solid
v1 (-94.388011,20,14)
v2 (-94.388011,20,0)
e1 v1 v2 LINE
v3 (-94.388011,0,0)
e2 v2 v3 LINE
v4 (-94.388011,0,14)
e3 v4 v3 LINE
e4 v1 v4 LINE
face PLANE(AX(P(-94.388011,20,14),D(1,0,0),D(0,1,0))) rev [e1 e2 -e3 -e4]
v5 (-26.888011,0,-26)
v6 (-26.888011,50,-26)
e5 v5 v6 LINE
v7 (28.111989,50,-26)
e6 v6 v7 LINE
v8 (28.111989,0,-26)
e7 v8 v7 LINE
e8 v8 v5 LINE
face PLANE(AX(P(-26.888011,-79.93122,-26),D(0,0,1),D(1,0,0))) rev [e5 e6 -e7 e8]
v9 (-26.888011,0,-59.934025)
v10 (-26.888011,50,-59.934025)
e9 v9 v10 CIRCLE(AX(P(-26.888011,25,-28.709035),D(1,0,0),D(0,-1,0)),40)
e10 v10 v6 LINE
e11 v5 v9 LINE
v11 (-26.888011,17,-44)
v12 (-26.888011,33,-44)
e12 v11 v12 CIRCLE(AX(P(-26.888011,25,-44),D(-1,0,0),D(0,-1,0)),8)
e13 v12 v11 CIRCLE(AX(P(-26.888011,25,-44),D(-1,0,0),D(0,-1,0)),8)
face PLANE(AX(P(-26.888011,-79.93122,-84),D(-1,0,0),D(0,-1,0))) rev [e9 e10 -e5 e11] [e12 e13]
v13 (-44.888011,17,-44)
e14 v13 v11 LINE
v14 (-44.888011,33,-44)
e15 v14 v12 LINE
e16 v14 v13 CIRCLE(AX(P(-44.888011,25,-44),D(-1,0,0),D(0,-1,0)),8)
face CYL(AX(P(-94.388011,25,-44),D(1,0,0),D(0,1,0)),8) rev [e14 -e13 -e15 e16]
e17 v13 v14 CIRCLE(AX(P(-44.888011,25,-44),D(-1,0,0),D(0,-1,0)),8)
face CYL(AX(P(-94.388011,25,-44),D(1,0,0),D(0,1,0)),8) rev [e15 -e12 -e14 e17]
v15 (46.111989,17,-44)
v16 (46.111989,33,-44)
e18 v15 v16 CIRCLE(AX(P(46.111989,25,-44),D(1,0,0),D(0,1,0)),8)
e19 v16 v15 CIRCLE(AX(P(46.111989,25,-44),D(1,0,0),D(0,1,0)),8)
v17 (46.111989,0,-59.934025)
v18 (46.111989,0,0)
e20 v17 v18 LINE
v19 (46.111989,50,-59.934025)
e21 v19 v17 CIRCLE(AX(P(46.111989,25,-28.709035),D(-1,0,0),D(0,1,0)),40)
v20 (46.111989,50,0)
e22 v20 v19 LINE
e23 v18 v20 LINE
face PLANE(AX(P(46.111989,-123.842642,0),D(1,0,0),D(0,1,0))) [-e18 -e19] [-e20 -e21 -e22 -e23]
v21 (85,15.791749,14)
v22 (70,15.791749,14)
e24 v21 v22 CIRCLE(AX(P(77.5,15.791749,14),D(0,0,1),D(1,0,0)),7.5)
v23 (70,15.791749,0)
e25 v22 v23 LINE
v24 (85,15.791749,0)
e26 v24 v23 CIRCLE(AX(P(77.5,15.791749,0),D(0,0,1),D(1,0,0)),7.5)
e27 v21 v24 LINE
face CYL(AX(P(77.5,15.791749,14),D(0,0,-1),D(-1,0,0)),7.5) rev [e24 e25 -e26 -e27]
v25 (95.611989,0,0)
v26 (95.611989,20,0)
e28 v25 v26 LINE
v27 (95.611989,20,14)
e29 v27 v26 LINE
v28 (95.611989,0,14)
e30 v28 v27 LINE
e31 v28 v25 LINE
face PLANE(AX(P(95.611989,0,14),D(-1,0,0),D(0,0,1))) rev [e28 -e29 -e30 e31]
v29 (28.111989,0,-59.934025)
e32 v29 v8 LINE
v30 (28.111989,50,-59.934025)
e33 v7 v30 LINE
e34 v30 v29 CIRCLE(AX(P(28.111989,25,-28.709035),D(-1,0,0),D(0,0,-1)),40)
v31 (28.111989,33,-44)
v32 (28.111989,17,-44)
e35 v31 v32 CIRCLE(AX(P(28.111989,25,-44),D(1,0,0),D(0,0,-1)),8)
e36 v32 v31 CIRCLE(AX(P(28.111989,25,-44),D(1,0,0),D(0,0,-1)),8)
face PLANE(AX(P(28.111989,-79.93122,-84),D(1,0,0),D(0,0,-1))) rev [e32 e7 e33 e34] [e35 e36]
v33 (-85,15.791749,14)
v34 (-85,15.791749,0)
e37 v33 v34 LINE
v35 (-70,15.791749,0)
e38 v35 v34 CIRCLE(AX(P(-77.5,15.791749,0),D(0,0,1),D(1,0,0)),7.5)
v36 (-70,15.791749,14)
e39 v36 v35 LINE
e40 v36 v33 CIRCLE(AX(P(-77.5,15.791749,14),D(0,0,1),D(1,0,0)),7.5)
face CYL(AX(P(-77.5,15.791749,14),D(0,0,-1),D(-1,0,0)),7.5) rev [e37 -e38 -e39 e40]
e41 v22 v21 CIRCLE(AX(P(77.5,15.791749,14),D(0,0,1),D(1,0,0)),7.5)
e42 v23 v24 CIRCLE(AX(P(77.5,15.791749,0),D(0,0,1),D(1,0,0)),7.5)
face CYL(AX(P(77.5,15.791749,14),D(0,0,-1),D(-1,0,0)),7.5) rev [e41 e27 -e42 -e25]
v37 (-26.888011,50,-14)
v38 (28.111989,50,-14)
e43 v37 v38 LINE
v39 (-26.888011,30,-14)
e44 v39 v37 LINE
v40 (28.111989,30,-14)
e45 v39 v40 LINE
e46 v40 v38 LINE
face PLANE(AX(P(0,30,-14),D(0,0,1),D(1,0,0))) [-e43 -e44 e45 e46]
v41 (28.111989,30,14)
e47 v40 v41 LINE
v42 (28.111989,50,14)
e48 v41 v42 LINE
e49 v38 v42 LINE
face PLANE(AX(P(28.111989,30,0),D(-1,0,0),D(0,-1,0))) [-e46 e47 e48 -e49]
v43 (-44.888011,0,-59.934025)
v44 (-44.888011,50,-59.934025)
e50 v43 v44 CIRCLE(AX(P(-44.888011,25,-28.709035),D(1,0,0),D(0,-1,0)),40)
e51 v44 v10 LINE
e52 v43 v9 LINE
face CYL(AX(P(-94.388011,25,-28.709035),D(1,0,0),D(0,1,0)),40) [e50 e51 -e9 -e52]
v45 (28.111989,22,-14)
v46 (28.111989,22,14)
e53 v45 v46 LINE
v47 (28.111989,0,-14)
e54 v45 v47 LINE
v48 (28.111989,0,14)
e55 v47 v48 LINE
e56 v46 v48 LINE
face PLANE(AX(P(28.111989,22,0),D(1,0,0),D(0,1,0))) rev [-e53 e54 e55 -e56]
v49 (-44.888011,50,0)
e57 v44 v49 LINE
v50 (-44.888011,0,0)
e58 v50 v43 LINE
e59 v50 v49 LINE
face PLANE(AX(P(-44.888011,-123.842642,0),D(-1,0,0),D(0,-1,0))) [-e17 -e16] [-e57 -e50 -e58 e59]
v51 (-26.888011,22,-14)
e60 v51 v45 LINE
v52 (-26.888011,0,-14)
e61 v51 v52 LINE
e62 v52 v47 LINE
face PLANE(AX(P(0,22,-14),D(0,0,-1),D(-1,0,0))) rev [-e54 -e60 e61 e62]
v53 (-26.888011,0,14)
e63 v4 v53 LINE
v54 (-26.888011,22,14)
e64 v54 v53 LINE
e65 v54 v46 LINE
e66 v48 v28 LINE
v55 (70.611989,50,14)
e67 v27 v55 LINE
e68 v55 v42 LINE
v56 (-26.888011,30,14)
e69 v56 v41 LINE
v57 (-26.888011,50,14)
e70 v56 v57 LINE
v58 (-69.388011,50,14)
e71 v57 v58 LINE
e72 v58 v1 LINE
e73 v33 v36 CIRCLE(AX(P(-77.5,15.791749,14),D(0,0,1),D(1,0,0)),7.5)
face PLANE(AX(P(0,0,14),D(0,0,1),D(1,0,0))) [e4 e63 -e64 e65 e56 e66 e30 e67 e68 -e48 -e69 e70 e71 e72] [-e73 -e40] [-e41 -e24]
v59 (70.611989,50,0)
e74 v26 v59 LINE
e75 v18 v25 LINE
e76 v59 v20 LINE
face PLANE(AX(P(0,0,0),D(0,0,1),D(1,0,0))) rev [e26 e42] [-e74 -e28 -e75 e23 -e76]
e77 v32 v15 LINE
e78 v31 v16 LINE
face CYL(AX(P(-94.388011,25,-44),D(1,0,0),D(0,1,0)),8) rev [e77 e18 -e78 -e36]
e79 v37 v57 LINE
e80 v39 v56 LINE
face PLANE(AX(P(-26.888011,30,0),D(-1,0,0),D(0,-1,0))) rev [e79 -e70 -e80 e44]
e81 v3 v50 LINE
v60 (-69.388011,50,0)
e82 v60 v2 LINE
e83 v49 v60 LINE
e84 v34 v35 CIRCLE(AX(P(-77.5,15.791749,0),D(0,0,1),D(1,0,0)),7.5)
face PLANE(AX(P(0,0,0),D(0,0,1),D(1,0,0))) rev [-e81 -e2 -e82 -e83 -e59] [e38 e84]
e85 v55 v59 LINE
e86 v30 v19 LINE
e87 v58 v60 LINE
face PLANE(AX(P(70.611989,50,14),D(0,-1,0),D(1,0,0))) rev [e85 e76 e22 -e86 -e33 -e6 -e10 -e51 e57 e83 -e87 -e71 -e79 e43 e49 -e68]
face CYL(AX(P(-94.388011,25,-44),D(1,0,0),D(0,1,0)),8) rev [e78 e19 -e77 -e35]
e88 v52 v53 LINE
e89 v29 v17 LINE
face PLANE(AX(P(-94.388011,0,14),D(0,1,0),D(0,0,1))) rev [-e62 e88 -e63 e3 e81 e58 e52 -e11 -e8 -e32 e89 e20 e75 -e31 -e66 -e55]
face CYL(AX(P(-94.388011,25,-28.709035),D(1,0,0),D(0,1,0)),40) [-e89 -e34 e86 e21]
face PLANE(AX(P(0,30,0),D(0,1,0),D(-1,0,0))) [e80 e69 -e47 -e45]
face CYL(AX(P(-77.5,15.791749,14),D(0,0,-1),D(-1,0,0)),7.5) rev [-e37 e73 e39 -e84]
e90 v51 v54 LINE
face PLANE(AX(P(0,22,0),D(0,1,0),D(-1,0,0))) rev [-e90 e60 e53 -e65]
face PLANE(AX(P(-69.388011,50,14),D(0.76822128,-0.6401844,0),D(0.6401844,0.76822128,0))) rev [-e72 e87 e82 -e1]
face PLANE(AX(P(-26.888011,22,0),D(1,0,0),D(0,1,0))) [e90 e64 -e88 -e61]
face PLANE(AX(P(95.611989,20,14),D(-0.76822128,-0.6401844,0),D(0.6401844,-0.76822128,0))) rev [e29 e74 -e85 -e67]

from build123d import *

# Parameters (mm, degrees)
LUG_PLATE_PROFILE_SKETCH_R   = 7.5
LUG_PLATE_PROFILE_14MM_DEPTH = 14
CROSS_BLOCK_SKETCH_W         = 91
CROSS_BLOCK_SKETCH_H         = 84
CROSS_BLOCK_91X84_DEPTH      = 50
CENTRE_POCKET_SKETCH_W       = 55
CENTRE_POCKET_SKETCH_H       = 58
CENTRE_POCKET_55X58_DEPTH    = 50
CLEARANCE_CUT_SKETCH_R       = 8
CLEARANCE_CUT_DEPTH          = 172.161473469
LUG_PIN_HOLES_SKETCH_W       = 55
LUG_PIN_HOLES_SKETCH_H       = 28
LUG_PIN_HOLE_CUT_20MM_DEPTH  = 20
LUG_START                    = -50
SKETCH7_4_W                  = 55
SKETCH7_4_H                  = 28
LUG_PIN_HOLE_CUT_22MM_DEPTH  = 22


with BuildPart() as part:
    # Lug Plate Profile Sketch → Lug Plate Profile 14mm (new body)
    with BuildSketch(Plane.XY):
        Polygon((-94.388010718, 0), (95.611989282, 0), (95.611989282, 20), (70.611989282, 50), (-69.388010718, 50), (-94.388010718, 20), align=None)
        with Locations((-77.5, 15.791749187)):
            Circle(LUG_PLATE_PROFILE_SKETCH_R, mode=Mode.SUBTRACT)
        with Locations((77.5, 15.791749187)):
            Circle(LUG_PLATE_PROFILE_SKETCH_R, mode=Mode.SUBTRACT)
    extrude(amount=LUG_PLATE_PROFILE_14MM_DEPTH)

    # Cross Block Sketch → Cross Block 91x84 (add)
    with BuildSketch(Plane(origin=(0, 50, 0), x_dir=(1, 0, 0), z_dir=(0, 1, 0))):
        with Locations((0.611989282, 42)):
            Rectangle(CROSS_BLOCK_SKETCH_W, CROSS_BLOCK_SKETCH_H)
    extrude(amount=-CROSS_BLOCK_91X84_DEPTH)

    # Centre Pocket Sketch → Centre Pocket 55x58 (cut)
    with BuildSketch(Plane(origin=(0, 50, 0), x_dir=(1, 0, 0), z_dir=(0, 1, 0))):
        with Locations((0.611989282, 55)):
            Rectangle(CENTRE_POCKET_SKETCH_W, CENTRE_POCKET_SKETCH_H)
    extrude(amount=-CENTRE_POCKET_55X58_DEPTH, mode=Mode.SUBTRACT)

    # Clearance Cut Sketch → Clearance Cut (cut, through all)
    with BuildSketch(Plane(origin=(46.111989282, 0, 0), x_dir=(0, 0, -1), z_dir=(1, 0, 0))):
        with Locations(Location((44, 25, 0), (0, 0, 90))):
            Circle(CLEARANCE_CUT_SKETCH_R)
        with BuildLine():
            ThreePointArc((59.934024659, 50), (68.709034667, 25), (59.934024659, 0))
            Line((59.934024659, 0), (84, 0))
            Line((84, 0), (84, 50))
            Line((84, 50), (59.934024659, 50))
        make_face()
    extrude(amount=-CLEARANCE_CUT_DEPTH, mode=Mode.SUBTRACT)

    # Lug Pin Holes Sketch → Lug Pin Hole Cut 20mm (cut)
    with BuildSketch(Plane(origin=(0, 50, 0), x_dir=(1, 0, 0), z_dir=(0, 1, 0))):
        with Locations((0.611989282, 0)):
            Rectangle(LUG_PIN_HOLES_SKETCH_W, LUG_PIN_HOLES_SKETCH_H)
    extrude(amount=-LUG_PIN_HOLE_CUT_20MM_DEPTH, mode=Mode.SUBTRACT)

    # Sketch7_4 → Lug Pin Hole Cut 22mm (cut)
    with BuildSketch(Plane(origin=(0, 50, 0), x_dir=(1, 0, 0), z_dir=(0, 1, 0)).offset(LUG_START)):
        with Locations((0.611989282, 0)):
            Rectangle(SKETCH7_4_W, SKETCH7_4_H)
    extrude(amount=LUG_PIN_HOLE_CUT_22MM_DEPTH, mode=Mode.SUBTRACT)


solid = part.part
